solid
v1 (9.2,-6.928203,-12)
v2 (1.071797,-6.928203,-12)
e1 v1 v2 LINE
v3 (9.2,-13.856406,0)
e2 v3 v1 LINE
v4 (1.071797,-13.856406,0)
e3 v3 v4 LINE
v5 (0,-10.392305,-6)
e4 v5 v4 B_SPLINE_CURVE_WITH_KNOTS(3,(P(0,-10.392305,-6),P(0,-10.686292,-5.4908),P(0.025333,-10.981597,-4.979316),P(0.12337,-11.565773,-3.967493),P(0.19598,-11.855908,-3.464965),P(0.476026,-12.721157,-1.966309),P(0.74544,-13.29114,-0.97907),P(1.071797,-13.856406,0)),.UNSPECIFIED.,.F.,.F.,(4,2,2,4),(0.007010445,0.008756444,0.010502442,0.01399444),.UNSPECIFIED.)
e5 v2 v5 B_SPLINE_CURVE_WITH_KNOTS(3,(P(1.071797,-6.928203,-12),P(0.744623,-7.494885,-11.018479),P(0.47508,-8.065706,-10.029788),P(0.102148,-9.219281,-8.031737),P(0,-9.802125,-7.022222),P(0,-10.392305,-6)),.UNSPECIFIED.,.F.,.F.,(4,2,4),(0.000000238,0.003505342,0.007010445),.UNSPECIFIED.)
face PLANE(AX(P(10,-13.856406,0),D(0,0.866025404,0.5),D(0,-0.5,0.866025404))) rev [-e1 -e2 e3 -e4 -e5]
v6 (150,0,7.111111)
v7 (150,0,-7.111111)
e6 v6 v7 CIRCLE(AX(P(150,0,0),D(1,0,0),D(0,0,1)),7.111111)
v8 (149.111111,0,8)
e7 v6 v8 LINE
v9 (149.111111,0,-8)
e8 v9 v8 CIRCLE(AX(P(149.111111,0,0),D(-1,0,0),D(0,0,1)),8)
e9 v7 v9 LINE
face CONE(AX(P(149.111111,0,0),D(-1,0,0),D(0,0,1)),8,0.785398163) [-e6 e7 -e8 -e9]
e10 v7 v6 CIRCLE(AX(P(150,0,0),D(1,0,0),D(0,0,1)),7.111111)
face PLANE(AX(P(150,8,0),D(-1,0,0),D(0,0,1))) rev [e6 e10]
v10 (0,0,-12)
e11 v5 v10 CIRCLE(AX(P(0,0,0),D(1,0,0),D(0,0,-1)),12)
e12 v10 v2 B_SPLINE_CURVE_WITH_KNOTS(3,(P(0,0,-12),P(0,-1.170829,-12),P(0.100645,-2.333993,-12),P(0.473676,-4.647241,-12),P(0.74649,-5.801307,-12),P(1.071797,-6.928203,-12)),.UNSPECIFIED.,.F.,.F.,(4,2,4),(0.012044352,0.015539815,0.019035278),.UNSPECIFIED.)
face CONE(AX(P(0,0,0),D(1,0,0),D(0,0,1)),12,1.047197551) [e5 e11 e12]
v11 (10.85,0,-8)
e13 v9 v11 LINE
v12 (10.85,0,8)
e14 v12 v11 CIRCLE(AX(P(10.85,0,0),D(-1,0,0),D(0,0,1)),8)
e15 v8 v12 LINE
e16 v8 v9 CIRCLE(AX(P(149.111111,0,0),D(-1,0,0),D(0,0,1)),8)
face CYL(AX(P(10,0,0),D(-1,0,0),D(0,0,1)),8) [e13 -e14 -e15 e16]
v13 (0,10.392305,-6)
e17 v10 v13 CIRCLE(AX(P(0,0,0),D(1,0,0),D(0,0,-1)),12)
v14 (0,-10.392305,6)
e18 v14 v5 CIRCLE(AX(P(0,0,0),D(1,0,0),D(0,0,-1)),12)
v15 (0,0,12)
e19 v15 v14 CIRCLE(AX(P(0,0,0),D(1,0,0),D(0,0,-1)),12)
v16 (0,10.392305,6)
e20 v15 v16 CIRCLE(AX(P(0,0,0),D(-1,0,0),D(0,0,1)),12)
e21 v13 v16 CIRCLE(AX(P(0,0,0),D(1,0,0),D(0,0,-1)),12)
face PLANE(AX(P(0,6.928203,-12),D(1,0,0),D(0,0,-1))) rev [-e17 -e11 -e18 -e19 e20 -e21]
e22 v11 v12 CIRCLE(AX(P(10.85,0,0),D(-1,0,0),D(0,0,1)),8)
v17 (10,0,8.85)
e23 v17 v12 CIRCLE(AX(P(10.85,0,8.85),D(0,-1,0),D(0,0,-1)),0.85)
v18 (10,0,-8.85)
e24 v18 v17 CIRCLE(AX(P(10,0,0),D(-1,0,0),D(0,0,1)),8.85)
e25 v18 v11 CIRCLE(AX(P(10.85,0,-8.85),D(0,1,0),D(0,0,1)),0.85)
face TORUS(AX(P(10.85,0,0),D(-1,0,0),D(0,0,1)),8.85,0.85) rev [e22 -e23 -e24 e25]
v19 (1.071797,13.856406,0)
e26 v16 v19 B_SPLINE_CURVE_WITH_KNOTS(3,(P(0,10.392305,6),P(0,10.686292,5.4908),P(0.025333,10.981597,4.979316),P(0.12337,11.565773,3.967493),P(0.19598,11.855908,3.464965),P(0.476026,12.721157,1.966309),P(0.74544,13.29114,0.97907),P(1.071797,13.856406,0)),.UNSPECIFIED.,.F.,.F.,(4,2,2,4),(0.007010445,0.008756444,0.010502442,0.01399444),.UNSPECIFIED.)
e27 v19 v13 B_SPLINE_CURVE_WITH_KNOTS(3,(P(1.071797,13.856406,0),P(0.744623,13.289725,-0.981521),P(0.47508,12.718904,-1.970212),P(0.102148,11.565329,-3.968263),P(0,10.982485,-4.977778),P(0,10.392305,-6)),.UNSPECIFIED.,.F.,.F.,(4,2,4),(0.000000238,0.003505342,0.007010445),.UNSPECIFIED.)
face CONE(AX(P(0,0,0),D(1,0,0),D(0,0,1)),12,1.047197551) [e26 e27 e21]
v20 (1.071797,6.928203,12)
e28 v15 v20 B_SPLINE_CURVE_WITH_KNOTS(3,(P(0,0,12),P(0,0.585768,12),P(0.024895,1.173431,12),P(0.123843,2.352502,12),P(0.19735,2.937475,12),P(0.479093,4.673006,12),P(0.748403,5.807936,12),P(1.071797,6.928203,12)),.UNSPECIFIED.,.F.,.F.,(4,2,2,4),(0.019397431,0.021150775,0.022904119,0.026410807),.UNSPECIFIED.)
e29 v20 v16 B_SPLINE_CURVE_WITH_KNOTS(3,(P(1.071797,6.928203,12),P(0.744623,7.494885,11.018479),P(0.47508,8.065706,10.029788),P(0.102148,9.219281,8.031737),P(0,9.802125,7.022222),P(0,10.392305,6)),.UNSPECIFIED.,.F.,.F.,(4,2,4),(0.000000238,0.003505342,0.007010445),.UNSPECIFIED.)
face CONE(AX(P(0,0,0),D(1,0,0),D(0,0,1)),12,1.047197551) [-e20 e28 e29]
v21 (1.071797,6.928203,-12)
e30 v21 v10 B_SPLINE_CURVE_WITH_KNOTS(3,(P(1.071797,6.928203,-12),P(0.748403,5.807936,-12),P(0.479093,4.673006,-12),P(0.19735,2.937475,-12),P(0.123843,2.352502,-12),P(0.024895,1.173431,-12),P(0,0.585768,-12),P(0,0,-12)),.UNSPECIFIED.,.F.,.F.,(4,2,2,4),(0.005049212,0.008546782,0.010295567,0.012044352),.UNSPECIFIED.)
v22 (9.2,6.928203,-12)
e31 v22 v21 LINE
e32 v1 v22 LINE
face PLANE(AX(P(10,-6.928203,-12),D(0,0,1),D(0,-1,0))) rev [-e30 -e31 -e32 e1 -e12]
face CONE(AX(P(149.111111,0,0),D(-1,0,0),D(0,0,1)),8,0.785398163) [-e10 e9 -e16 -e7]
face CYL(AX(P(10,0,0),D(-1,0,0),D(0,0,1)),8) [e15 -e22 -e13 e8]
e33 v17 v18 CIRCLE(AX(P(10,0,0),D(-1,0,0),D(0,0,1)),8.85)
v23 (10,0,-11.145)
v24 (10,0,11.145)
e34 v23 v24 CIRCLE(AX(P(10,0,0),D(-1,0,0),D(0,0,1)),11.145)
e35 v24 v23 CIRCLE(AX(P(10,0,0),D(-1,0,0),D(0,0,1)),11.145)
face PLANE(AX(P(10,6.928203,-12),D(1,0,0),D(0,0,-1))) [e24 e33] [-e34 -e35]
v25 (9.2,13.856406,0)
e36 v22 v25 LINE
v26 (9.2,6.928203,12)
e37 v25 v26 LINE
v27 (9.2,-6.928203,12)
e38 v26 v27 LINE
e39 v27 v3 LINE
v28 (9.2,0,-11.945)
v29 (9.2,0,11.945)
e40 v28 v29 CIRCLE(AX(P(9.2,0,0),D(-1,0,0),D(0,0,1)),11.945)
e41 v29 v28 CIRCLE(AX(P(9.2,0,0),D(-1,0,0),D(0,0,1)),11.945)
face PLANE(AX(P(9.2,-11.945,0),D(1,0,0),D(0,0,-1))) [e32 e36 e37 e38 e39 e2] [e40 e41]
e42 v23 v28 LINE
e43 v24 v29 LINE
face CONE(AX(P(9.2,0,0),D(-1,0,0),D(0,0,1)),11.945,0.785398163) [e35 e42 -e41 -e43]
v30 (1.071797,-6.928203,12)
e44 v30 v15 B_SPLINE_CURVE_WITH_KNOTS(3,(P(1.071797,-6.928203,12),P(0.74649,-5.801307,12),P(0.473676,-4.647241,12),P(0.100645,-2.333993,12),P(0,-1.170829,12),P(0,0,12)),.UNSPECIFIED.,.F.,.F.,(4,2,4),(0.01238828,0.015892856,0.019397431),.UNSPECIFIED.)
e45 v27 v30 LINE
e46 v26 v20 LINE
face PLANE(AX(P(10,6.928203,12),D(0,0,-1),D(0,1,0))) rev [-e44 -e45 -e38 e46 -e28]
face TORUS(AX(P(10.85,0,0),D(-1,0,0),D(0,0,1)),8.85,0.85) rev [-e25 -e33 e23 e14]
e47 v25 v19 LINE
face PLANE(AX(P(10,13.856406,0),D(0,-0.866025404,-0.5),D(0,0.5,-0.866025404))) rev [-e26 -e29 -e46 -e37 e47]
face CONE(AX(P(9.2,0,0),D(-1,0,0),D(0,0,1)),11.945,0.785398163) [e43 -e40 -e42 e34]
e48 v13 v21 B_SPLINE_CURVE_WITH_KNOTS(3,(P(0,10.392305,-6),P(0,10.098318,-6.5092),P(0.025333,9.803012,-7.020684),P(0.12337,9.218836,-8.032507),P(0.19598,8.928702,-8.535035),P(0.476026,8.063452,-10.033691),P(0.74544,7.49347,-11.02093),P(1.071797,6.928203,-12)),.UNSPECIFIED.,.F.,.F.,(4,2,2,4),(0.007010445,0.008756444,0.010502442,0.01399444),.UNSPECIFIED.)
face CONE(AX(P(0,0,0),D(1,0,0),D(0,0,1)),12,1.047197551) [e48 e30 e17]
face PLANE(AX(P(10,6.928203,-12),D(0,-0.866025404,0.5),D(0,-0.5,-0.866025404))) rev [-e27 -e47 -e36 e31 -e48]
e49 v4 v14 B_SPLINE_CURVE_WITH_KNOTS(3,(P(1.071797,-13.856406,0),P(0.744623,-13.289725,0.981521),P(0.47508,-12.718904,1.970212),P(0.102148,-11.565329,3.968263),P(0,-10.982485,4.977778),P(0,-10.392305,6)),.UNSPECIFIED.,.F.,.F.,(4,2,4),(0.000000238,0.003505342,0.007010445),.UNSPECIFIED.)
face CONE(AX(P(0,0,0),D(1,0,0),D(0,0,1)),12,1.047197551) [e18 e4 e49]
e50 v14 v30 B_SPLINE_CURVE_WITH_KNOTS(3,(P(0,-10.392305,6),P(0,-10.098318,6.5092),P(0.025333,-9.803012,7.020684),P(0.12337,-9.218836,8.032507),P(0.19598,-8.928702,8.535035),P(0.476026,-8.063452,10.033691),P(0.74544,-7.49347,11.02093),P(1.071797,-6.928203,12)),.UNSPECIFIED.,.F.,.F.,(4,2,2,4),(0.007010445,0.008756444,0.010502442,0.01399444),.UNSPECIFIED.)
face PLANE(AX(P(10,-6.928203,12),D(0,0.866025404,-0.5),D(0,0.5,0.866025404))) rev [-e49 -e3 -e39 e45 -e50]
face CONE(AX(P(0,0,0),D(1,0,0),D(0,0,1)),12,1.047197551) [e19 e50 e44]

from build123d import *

# Parameters (mm, degrees)
BOSS_EXTRUDE1_DEPTH = 10
SKETCH4_R           = 26.75
SKETCH4_R_2         = 12
CUT_EXTRUDE1_DEPTH  = 1.25
CUT_EXTRUDE1_DRAFT  = -60
CHAMFER2_SIZE       = 0.888888889


with BuildPart() as part:
    # Sketch3 → Boss-Extrude1 (new body)
    with BuildSketch(Plane(origin=(0, 0, 0), x_dir=(0, 0, -1), z_dir=(1, 0, 0))):
        Polygon((12, 6.92820323), (0, 13.856406461), (-12, 6.92820323), (-12, -6.92820323), (0, -13.856406461), (12, -6.92820323), align=None)
    extrude(amount=BOSS_EXTRUDE1_DEPTH)


with BuildPart() as cut_extrude1_tool:
    # Sketch4 → Cut-Extrude1 (with draft: the straight prism first)
    with BuildSketch(Plane.ZY):
        Circle(SKETCH4_R)
        Circle(SKETCH4_R_2, mode=Mode.SUBTRACT)
    extrude(amount=-CUT_EXTRUDE1_DEPTH)
    # Cut-Extrude1: the draft: its side faces are tilted about the plane it starts from
    cut_extrude1_sides = [cut_extrude1_tool.faces().sort_by_distance(p)[0] for p in [
        (0.625, 0, -26.75),
        (0.625, 0, -12),
    ]]
    draft(cut_extrude1_sides, Plane.ZY, CUT_EXTRUDE1_DRAFT)


with BuildPart() as part_1:
    add(part.part)

    # Cut-Extrude1: cut by cut_extrude1_tool
    add(cut_extrude1_tool.part, mode=Mode.SUBTRACT)

    # Sketch5 → Revolve1 (revolve)
    with BuildSketch(Plane.XY, mode=Mode.PRIVATE) as revolve1_sk:
        with BuildLine():
            Line((10.85, 8), (150, 8))
            Line((150, 8), (150, 0))
            Line((150, 0), (10, 0))
            Line((10, 0), (10, 8.85))
            ThreePointArc((10, 8.85), (10.248959236, 8.248959236), (10.85, 8))
        make_face()
    revolve(revolve1_sk.sketch.rotate(Axis((10, 0, 0), (1, 0, 0)), 90), axis=Axis((10, 0, 0), (1, 0, 0)))

    # Chamfer2
    chamfer2_edges = [part_1.edges().sort_by_distance(p)[0] for p in [
        (150, 0, -8),
    ]]
    chamfer(chamfer2_edges, length=CHAMFER2_SIZE)

    # Sketch7 → Cut-Revolve1 (revolve, cut)
    with BuildSketch(Plane.XY, mode=Mode.PRIVATE) as cut_revolve1_sk:
        Polygon((10, 11.145), (9.2, 11.945), (9.2, 26.75), (10, 26.75), align=None)
    revolve(cut_revolve1_sk.sketch.rotate(Axis((0, 0, 0), (1, 0, 0)), 90), axis=Axis((0, 0, 0), (1, 0, 0)), mode=Mode.SUBTRACT)


solid = part_1.part
